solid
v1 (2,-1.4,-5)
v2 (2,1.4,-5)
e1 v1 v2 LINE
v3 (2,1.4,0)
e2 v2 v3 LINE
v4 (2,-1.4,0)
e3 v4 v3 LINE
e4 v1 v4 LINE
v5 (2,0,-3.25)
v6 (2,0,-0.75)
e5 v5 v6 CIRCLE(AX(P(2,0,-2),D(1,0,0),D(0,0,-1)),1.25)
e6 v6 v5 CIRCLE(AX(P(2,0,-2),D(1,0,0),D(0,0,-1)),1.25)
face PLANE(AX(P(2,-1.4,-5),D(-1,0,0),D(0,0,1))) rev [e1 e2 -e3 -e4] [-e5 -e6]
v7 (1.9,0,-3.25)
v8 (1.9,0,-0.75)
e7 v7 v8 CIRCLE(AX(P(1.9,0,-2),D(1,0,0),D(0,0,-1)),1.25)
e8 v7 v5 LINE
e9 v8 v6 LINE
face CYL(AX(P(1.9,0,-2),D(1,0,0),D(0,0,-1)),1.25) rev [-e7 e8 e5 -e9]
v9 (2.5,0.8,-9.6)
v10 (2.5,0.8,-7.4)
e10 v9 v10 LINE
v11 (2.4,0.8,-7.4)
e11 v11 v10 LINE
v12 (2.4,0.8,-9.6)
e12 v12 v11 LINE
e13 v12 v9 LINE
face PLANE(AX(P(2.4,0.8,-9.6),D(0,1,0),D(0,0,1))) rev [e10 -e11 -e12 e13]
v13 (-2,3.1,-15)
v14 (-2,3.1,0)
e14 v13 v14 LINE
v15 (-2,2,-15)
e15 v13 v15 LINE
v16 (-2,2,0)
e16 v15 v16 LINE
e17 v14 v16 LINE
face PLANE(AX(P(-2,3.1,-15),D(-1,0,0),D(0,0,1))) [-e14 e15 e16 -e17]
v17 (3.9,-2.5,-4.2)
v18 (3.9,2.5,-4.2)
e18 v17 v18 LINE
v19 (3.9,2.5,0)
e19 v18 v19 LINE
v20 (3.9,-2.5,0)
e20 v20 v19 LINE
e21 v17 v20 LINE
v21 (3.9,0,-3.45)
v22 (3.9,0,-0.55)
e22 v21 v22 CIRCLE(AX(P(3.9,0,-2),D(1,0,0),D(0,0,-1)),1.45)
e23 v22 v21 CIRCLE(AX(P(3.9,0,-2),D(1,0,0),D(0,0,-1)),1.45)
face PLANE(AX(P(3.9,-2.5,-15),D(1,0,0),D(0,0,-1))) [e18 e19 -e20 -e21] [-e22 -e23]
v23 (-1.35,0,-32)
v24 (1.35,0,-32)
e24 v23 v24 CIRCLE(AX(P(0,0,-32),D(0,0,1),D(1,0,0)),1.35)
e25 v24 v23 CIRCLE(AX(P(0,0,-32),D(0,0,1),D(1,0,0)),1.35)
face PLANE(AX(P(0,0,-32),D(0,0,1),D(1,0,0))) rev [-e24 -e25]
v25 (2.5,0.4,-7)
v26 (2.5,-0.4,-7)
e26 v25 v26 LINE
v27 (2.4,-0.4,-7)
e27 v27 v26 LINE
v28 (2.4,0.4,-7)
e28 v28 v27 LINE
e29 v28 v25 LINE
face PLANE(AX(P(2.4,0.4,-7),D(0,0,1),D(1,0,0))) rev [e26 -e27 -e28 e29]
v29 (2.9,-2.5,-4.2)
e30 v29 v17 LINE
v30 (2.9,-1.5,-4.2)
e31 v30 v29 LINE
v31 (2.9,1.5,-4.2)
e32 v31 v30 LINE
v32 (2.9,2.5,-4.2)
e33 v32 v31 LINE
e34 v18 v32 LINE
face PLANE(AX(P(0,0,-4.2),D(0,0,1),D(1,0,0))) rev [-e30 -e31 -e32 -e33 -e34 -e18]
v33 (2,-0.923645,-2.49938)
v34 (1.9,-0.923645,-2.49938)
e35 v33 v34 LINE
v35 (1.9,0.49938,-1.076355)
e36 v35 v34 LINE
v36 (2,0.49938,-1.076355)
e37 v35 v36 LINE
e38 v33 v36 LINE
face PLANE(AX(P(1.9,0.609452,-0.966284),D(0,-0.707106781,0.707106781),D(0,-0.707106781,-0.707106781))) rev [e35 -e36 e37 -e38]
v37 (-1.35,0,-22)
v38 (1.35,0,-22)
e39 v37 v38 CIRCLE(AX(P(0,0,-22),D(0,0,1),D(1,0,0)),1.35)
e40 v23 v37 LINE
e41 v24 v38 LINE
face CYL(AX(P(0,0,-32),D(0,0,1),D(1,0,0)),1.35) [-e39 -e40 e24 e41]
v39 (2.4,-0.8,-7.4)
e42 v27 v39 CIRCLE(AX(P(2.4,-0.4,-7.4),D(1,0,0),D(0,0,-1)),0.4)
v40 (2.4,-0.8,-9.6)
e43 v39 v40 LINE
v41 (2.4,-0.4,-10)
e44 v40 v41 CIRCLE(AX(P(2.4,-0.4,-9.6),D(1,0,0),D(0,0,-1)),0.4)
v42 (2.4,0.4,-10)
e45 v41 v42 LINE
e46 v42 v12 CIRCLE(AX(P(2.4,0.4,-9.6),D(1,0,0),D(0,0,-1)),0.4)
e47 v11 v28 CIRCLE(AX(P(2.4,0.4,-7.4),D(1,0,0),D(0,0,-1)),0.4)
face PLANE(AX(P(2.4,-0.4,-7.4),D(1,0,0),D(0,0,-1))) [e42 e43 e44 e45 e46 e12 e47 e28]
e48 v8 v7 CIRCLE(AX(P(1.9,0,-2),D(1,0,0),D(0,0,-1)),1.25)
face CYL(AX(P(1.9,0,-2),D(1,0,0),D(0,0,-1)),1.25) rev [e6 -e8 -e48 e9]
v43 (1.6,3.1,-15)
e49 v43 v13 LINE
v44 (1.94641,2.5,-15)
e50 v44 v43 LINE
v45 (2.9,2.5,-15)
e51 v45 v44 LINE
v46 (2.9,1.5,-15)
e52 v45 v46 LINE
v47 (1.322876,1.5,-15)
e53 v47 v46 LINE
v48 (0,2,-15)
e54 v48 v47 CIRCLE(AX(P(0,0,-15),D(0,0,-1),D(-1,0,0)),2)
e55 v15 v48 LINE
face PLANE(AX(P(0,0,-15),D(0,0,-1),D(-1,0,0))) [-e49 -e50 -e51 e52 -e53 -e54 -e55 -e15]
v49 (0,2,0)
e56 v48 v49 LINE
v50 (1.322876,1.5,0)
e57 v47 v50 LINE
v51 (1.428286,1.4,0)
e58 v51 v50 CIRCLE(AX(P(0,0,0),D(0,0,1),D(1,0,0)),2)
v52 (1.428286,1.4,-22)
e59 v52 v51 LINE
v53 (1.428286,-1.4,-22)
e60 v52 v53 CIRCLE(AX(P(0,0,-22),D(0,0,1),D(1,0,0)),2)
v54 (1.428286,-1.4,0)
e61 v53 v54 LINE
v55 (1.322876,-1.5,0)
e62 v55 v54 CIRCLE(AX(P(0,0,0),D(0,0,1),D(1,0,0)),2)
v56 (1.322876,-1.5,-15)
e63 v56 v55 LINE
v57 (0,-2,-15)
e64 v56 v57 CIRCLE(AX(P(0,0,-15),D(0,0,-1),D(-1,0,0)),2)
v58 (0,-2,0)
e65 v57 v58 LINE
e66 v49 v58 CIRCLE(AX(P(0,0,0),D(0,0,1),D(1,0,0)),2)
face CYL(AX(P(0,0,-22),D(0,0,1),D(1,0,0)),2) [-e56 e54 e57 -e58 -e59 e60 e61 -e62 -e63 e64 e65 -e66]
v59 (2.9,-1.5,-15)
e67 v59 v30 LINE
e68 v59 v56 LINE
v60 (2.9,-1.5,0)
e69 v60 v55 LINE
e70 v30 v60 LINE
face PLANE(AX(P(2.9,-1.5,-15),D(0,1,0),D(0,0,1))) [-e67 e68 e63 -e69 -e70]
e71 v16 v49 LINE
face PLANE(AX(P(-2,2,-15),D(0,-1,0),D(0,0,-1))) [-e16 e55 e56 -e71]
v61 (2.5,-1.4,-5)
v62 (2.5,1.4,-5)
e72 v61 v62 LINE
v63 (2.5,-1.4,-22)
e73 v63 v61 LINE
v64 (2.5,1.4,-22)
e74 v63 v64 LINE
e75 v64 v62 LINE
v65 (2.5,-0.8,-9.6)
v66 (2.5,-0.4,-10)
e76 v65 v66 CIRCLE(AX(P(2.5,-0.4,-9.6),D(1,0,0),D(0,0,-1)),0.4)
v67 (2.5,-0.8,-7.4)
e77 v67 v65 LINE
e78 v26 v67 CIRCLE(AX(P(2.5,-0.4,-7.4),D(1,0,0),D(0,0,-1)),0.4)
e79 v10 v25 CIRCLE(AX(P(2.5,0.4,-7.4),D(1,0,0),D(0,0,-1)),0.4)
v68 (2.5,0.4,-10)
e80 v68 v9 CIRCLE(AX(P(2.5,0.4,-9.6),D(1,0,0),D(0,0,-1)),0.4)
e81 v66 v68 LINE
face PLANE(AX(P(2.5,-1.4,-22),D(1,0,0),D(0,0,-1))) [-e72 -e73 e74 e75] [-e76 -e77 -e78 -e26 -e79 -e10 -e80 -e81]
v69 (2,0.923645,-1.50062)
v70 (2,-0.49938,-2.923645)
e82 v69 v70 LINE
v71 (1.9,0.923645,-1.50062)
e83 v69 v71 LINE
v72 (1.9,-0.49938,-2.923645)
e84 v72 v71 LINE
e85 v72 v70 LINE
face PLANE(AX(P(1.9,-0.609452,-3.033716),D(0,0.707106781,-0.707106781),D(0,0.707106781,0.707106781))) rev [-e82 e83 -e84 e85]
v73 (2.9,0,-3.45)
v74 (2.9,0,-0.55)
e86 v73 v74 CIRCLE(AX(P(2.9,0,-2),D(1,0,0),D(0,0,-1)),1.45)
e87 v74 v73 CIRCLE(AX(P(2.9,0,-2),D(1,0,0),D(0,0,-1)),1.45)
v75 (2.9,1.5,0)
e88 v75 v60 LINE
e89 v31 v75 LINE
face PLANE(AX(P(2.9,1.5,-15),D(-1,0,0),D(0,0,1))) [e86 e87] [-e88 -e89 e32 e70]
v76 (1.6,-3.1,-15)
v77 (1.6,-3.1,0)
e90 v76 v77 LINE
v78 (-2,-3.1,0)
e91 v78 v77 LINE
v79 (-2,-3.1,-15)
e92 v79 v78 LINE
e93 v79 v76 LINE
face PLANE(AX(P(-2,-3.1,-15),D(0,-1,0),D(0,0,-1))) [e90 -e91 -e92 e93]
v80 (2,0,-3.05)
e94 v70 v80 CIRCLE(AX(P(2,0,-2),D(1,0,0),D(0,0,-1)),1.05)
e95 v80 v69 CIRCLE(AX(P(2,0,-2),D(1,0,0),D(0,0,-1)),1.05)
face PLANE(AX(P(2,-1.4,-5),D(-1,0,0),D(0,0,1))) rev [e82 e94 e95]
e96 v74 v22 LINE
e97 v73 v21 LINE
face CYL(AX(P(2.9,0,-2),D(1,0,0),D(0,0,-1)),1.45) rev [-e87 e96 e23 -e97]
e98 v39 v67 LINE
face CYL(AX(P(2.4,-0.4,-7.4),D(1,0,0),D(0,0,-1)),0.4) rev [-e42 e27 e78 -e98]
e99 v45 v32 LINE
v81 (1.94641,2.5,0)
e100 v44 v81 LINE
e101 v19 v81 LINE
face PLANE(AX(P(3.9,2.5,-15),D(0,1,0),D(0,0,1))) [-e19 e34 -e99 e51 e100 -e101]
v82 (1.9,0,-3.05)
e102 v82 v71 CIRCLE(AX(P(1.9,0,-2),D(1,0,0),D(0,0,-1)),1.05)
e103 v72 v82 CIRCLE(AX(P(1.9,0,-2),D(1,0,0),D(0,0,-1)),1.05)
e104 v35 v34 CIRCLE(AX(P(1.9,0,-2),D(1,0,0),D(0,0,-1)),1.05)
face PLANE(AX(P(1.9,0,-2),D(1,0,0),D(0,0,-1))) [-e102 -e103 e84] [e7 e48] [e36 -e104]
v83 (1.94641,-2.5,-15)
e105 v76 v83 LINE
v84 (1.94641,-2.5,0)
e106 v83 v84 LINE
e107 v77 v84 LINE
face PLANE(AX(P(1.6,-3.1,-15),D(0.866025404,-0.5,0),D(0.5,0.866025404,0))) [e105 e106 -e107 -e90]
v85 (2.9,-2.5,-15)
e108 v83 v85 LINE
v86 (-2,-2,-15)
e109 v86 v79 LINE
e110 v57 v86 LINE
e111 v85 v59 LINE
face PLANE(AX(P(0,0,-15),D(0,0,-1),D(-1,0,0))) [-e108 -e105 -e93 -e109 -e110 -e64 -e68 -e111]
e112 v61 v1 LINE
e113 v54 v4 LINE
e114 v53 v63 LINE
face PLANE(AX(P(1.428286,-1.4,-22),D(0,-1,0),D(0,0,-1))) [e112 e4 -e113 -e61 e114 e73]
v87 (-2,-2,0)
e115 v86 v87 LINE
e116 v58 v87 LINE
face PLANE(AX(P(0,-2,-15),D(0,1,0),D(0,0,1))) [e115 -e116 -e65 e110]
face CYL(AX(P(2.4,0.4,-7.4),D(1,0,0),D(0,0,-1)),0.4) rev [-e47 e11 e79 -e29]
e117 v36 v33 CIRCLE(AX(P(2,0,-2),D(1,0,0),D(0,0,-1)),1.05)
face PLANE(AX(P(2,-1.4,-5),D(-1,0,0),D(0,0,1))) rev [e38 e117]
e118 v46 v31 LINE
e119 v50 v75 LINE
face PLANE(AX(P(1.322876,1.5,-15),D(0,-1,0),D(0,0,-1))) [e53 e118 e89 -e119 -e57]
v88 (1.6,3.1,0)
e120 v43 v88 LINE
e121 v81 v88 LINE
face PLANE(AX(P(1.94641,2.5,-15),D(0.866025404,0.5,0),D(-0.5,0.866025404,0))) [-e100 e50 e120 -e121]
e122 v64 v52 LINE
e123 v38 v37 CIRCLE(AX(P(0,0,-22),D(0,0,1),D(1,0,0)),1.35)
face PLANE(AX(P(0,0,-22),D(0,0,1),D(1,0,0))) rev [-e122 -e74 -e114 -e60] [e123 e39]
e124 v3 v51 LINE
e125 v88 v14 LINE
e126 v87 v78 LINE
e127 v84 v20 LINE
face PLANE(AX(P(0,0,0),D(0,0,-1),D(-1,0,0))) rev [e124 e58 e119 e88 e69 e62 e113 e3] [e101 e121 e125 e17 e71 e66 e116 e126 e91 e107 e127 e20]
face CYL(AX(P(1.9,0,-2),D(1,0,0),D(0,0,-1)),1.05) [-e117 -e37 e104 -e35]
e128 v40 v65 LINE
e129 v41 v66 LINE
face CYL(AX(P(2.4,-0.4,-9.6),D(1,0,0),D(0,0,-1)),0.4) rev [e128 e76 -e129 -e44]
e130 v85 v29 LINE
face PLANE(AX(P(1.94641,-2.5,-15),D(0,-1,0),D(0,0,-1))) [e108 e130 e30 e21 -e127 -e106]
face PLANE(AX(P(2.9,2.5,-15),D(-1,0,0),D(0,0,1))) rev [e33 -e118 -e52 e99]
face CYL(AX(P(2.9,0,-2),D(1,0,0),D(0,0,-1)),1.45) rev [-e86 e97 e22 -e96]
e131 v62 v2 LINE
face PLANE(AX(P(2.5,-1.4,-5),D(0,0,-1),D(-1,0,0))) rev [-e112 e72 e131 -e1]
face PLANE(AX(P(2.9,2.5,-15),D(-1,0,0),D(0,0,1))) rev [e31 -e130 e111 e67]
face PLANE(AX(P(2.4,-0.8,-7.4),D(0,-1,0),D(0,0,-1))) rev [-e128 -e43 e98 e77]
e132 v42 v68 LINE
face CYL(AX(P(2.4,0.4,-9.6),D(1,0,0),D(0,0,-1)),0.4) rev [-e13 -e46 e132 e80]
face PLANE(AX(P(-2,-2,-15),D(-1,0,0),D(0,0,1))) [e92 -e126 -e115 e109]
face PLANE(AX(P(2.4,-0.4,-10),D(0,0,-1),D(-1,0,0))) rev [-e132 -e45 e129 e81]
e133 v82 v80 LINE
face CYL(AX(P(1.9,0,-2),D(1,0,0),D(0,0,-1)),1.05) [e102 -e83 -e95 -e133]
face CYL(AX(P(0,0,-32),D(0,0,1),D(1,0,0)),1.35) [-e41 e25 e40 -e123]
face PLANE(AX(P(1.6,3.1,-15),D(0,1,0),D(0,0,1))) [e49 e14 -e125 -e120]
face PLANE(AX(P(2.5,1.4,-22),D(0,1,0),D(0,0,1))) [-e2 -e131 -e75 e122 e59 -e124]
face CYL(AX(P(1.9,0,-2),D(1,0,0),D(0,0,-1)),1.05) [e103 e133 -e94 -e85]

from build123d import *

# Parameters (mm, degrees)
EXTRUDE_1_DEPTH          = 15
SKETCH_2_W               = 1
SKETCH_2_H               = 5
CUT_EXTRUDE_1_DEPTH      = 10.8
SKETCH_3_R               = 1.45
CUT_EXTRUDE_2_DEPTH      = 1
EXTRUDE_2_DEPTH          = 22
CUT_EXTRUDE_3_DEPTH      = 1.4
CUT_EXTRUDE_3_DEPTH_BACK = 1.4
SKETCH_5_W               = 0.5
SKETCH_5_H               = 5
SKETCH_6_R               = 1.25
SKETCH_6_R_2             = 1.05
CUT_EXTRUDE_4_DEPTH      = 0.1
CUT_EXTRUDE_5_DEPTH      = 0.1
CUT_EXTRUDE_6_DEPTH      = 0.1
SKETCH_9_R               = 1.35
EXTRUDE_3_DEPTH          = 10


with BuildPart() as part:
    # 草图1 → 凸台-拉伸1 (new body)
    with BuildSketch(Plane.XY):
        with BuildLine():
            Line((-2, -3.1), (1.6, -3.1))
            Line((1.6, -3.1), (1.946410162, -2.5))
            Line((1.946410162, -2.5), (3.9, -2.5))
            Line((3.9, -2.5), (3.9, 2.5))
            Line((3.9, 2.5), (1.946410162, 2.5))
            Line((1.946410162, 2.5), (1.6, 3.1))
            Line((1.6, 3.1), (-2, 3.1))
            Line((-2, 3.1), (-2, 2))
            Line((-2, 2), (0, 2))
            ThreePointArc((0, 2), (0.707106781, 1.870828693), (1.322875656, 1.5))
            Line((1.322875656, 1.5), (2.9, 1.5))
            Line((2.9, 1.5), (2.9, -1.5))
            Line((2.9, -1.5), (1.322875656, -1.5))
            ThreePointArc((1.322875656, -1.5), (0.707106781, -1.870828693), (0, -2))
            Line((0, -2), (-2, -2))
            Line((-2, -2), (-2, -3.1))
        make_face()
    extrude(amount=-EXTRUDE_1_DEPTH)

    # 草图2 → 切除-拉伸1 (cut)
    with BuildSketch(Plane.XY.offset(-4.2)):
        with Locations((3.4, 0)):
            Rectangle(SKETCH_2_W, SKETCH_2_H)
    extrude(amount=-CUT_EXTRUDE_1_DEPTH, mode=Mode.SUBTRACT)

    # 草图3 → 切除-拉伸2 (cut)
    with BuildSketch(Plane(origin=(3.9, 0, 0), x_dir=(0, 0, -1), z_dir=(1, 0, 0))):
        with Locations((2, 0)):
            Circle(SKETCH_3_R)
    extrude(amount=-CUT_EXTRUDE_2_DEPTH, mode=Mode.SUBTRACT)

    # 草图4 → 凸台-拉伸2 (add)
    with BuildSketch(Plane.XY):
        with BuildLine():
            Line((1.428285686, -1.4), (2.5, -1.4))
            Line((2.5, -1.4), (2.5, 1.4))
            Line((2.5, 1.4), (1.428285686, 1.4))
            ThreePointArc((1.428285686, 1.4), (-2, 0), (1.428285686, -1.4))
        make_face()
    extrude(amount=-EXTRUDE_2_DEPTH)

    # 草图5 → 切除-拉伸3 (cut, two sides: drawn at the far end of the back side and taken through both)
    with BuildSketch(Plane(origin=(0, 0, 0), x_dir=(1, 0, 0), z_dir=(0, 1, 0)).offset(-CUT_EXTRUDE_3_DEPTH_BACK)):
        with Locations((2.25, 2.5)):
            Rectangle(SKETCH_5_W, SKETCH_5_H)
    extrude(amount=CUT_EXTRUDE_3_DEPTH + CUT_EXTRUDE_3_DEPTH_BACK, mode=Mode.SUBTRACT)

    # 草图6 → 切除-拉伸4 (cut)
    with BuildSketch(Plane(origin=(2, 0, 0), x_dir=(0, 0, -1), z_dir=(1, 0, 0))):
        with Locations((2, 0)):
            Circle(SKETCH_6_R)
        with Locations((2, 0)):
            Circle(SKETCH_6_R_2, mode=Mode.SUBTRACT)
    extrude(amount=-CUT_EXTRUDE_4_DEPTH, mode=Mode.SUBTRACT)

    # 草图7 → 切除-拉伸5 (cut)
    with BuildSketch(Plane(origin=(2, 0, 0), x_dir=(0, 0, -1), z_dir=(1, 0, 0))):
        with BuildLine():
            Line((0.966284129, 0.609451802), (2.609451802, -1.033715871))
            ThreePointArc((2.609451802, -1.033715871), (2.848528137, -0.848528137), (3.033715871, -0.609451802))
            Line((3.033715871, -0.609451802), (1.390548198, 1.033715871))
            ThreePointArc((1.390548198, 1.033715871), (1.151471863, 0.848528137), (0.966284129, 0.609451802))
        make_face()
    extrude(amount=-CUT_EXTRUDE_5_DEPTH, mode=Mode.SUBTRACT)

    # 草图8 → 切除-拉伸6 (cut)
    with BuildSketch(Plane(origin=(2.5, 0, 0), x_dir=(0, 0, -1), z_dir=(1, 0, 0))):
        with BuildLine():
            Line((7.4, -0.8), (9.6, -0.8))
            ThreePointArc((9.6, -0.8), (9.882842712, -0.682842712), (10, -0.4))
            Line((10, -0.4), (10, 0.4))
            ThreePointArc((10, 0.4), (9.882842712, 0.682842712), (9.6, 0.8))
            Line((9.6, 0.8), (7.4, 0.8))
            ThreePointArc((7.4, 0.8), (7.117157288, 0.682842712), (7, 0.4))
            Line((7, 0.4), (7, -0.4))
            ThreePointArc((7, -0.4), (7.117157288, -0.682842712), (7.4, -0.8))
        make_face()
    extrude(amount=-CUT_EXTRUDE_6_DEPTH, mode=Mode.SUBTRACT)

    # 草图9 → 凸台-拉伸3 (add)
    with BuildSketch(Plane.XY.offset(-22)):
        Circle(SKETCH_9_R)
    extrude(amount=-EXTRUDE_3_DEPTH)


solid = part.part
